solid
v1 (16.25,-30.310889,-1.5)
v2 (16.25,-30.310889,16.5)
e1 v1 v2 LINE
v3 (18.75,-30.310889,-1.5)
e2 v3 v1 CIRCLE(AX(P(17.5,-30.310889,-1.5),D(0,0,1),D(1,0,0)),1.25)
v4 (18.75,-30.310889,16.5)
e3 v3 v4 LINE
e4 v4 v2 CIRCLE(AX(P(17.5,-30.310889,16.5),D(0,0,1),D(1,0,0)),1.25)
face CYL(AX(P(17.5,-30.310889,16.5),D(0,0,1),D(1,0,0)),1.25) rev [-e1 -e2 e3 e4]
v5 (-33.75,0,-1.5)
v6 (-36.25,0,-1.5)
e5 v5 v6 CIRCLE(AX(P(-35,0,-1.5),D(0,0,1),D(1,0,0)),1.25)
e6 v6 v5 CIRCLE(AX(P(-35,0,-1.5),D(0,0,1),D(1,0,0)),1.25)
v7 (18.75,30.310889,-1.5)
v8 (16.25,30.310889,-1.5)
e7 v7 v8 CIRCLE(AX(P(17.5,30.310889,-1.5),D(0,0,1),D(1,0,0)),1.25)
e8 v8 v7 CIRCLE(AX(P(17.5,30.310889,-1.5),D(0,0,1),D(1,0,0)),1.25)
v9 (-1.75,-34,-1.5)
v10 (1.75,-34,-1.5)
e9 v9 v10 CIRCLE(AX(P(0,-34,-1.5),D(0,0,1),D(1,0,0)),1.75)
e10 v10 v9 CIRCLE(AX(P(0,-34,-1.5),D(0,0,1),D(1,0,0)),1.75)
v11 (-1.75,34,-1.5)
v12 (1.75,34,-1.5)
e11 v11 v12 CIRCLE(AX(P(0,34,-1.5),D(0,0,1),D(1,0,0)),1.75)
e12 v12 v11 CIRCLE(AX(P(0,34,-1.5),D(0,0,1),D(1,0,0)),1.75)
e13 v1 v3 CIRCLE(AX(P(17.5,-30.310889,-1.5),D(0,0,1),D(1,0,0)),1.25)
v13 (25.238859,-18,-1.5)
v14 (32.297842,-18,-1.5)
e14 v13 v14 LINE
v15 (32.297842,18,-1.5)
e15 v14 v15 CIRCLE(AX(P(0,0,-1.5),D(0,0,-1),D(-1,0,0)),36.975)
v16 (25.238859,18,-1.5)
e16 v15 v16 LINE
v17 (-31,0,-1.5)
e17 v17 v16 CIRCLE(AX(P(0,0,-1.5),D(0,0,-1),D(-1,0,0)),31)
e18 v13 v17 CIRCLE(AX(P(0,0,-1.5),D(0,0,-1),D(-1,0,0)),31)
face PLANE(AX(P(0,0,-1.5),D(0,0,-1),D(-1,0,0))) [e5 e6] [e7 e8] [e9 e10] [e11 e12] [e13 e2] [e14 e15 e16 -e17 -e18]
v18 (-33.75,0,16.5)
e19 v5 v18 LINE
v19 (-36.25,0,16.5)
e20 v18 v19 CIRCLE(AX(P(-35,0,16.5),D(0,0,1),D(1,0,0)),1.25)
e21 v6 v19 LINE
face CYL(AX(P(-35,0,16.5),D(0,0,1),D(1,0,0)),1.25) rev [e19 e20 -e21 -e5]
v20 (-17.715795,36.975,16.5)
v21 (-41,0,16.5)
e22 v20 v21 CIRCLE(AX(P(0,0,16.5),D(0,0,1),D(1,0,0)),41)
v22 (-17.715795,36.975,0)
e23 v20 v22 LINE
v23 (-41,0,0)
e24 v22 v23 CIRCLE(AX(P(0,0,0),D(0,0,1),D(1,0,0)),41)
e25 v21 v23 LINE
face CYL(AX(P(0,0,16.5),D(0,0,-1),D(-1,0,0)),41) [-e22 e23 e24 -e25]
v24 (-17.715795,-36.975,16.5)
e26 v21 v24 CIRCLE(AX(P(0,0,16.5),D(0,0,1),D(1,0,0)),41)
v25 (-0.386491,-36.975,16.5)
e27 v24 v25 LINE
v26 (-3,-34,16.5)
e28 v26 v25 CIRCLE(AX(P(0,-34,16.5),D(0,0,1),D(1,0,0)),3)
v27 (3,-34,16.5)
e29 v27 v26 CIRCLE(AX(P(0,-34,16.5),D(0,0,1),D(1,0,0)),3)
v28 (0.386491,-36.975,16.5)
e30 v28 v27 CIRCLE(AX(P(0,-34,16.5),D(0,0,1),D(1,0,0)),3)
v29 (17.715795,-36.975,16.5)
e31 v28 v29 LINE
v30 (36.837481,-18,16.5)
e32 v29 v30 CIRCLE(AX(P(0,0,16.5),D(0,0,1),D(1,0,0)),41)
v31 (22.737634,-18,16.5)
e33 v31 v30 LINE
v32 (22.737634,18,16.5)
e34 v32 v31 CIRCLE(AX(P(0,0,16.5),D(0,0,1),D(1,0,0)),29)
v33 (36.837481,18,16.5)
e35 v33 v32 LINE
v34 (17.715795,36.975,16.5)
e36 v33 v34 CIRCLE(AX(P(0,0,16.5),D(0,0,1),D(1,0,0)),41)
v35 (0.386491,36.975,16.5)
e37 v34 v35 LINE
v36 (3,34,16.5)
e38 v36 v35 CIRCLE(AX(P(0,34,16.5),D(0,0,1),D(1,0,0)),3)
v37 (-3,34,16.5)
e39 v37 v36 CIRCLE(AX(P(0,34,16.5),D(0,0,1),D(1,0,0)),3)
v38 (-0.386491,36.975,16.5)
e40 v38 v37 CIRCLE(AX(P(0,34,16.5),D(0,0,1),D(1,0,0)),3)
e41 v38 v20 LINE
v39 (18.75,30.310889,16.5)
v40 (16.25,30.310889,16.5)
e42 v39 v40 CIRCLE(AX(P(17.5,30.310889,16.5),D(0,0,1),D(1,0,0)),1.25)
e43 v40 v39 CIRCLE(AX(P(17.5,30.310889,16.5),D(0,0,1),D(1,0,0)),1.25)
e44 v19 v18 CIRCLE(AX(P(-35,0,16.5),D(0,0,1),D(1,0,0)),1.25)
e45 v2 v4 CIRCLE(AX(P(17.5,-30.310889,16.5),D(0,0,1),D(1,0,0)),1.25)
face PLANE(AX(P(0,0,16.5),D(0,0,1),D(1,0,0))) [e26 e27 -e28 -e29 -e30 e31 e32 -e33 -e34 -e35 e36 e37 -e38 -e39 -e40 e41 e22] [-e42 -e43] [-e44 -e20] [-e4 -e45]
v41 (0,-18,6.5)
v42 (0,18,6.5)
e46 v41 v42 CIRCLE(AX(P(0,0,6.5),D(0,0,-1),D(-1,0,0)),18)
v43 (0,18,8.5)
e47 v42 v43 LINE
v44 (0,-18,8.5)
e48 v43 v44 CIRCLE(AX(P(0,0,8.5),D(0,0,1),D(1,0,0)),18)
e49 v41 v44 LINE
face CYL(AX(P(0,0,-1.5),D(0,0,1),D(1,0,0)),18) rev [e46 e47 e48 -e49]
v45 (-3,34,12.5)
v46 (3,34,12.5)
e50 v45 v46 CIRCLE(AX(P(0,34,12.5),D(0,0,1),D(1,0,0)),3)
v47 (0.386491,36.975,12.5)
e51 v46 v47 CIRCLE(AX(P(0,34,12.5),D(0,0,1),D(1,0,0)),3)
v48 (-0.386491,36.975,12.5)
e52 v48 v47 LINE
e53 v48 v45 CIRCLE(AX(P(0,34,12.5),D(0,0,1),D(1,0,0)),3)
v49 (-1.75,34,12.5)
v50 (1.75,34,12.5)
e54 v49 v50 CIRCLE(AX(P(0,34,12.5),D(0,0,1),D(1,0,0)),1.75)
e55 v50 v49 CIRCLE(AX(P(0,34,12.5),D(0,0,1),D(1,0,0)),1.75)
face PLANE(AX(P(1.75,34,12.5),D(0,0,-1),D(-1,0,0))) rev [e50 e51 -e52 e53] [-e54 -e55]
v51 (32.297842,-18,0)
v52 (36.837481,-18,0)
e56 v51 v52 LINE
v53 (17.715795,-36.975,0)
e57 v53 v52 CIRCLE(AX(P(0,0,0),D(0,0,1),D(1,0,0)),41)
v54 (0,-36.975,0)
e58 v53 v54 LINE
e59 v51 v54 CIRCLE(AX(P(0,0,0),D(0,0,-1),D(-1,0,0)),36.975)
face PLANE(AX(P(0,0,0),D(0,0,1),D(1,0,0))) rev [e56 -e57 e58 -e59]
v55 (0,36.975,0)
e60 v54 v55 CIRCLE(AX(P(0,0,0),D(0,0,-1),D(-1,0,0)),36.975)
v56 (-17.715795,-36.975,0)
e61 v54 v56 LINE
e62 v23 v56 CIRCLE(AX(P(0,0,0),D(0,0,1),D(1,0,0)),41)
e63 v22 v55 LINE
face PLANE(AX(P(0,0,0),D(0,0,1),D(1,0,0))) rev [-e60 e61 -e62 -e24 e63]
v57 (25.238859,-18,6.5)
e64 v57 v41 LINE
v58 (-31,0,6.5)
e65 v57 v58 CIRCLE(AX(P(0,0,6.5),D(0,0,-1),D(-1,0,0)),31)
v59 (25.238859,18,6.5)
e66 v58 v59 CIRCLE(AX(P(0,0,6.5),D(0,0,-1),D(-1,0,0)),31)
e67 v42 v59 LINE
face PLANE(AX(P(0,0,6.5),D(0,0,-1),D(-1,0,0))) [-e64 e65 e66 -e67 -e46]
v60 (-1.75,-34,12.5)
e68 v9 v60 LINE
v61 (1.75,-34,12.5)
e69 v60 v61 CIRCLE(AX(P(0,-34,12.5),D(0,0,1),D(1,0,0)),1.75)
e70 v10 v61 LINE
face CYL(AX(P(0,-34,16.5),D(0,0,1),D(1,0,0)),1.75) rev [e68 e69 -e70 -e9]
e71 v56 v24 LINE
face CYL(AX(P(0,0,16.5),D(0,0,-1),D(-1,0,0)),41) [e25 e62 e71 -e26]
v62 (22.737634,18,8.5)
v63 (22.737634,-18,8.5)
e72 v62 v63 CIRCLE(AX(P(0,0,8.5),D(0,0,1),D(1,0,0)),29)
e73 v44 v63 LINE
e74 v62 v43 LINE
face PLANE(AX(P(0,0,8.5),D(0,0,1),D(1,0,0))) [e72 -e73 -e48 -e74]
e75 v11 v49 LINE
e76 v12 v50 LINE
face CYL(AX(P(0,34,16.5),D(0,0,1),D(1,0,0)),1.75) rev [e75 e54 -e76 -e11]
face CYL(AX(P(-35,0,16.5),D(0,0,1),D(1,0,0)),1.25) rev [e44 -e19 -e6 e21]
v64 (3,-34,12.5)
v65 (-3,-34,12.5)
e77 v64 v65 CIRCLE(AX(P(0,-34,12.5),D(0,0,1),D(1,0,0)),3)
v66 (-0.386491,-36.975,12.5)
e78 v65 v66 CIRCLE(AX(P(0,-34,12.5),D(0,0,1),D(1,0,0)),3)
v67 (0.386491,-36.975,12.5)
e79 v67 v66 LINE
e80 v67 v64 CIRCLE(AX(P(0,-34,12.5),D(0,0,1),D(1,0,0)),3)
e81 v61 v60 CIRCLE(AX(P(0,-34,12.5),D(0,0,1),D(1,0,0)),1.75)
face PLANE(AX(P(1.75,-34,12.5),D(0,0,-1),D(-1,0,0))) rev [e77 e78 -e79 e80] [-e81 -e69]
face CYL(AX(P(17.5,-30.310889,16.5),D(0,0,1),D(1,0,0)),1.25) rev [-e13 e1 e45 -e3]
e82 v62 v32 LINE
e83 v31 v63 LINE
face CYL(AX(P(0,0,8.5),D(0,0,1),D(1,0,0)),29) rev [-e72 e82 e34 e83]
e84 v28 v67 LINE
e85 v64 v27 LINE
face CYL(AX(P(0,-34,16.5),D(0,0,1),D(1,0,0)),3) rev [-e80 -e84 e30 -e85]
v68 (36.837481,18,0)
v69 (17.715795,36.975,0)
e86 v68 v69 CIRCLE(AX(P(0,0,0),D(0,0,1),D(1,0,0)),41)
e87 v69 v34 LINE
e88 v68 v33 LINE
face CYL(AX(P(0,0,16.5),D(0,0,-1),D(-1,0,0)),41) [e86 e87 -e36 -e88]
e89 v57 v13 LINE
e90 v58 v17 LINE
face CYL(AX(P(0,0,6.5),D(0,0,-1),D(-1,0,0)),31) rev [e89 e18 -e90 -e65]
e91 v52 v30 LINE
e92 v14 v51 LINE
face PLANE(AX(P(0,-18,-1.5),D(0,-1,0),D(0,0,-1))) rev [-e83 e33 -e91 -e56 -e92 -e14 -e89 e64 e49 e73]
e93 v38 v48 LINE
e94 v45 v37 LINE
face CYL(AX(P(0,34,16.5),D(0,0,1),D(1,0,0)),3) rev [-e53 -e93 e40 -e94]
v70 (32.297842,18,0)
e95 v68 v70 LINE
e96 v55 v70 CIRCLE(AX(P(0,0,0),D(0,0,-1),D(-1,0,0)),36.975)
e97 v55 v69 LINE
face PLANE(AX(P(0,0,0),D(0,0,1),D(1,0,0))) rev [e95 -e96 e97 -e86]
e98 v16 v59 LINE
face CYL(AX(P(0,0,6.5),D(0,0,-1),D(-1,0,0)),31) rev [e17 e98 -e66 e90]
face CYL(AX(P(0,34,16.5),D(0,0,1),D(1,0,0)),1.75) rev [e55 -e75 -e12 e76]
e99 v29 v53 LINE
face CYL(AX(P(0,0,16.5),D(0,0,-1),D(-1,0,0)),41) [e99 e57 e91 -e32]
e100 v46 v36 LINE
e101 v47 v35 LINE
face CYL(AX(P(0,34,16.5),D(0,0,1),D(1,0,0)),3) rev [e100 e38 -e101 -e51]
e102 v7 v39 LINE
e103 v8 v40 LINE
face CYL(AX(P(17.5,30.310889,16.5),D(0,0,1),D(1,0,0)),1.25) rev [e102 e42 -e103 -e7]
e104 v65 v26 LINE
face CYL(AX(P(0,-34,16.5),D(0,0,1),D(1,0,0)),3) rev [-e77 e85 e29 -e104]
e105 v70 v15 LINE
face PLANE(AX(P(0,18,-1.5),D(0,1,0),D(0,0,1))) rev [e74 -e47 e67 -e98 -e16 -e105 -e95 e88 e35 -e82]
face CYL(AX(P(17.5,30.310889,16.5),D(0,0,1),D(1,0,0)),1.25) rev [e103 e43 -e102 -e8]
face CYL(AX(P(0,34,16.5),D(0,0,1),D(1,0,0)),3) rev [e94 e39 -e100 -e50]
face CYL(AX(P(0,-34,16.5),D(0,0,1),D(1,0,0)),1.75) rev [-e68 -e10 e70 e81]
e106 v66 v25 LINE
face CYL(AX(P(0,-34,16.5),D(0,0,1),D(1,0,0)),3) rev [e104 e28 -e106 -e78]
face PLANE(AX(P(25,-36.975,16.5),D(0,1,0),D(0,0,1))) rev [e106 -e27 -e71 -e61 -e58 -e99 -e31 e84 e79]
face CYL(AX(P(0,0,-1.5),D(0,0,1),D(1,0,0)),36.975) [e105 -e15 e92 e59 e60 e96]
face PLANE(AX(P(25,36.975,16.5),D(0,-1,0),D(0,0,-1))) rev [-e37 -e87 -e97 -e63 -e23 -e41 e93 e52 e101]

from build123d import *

# Parameters (mm, degrees)
SKETCH1_R                               = 41
BOSS_EXTRUDE1_DEPTH                     = 16.5
SKETCH2_R                               = 36.975
BOSS_EXTRUDE2_DEPTH                     = 1.5
SKETCH4_W                               = 50
SKETCH4_H                               = 6.84002239
CUT_EXTRUDE1_DEPTH                      = 61.712436947
SKETCH5_R                               = 31
CUT_EXTRUDE3_DEPTH                      = 8
SKETCH6_R                               = 29
CUT_EXTRUDE4_DEPTH                      = 8
CUT_EXTRUDE5_DEPTH                      = 57.108382841
CUT_EXTRUDE5_DEPTH_BACK                 = 57.108382841
CBORE_FOR_M3_HEX_HEAD_BOLT3_D           = 3.5
CBORE_FOR_M3_HEX_HEAD_BOLT3_CBORE_D     = 6
CBORE_FOR_M3_HEX_HEAD_BOLT3_CBORE_DEPTH = 4
M3_TAPPED_HOLE1_D                       = 2.5
CIRPATTERN1_COUNT                       = 3


with BuildPart() as part:
    # Sketch1 → Boss-Extrude1 (new body)
    with BuildSketch(Plane.XY):
        Circle(SKETCH1_R)
    extrude(amount=BOSS_EXTRUDE1_DEPTH)

    # Sketch2 → Boss-Extrude2 (add)
    with BuildSketch(Plane(origin=(0, 0, 0), x_dir=(-1, 0, 0), z_dir=(0, 0, -1))):
        Circle(SKETCH2_R)
    extrude(amount=BOSS_EXTRUDE2_DEPTH)

    # Sketch4 → Cut-Extrude1 (cut, through all)
    with BuildSketch(Plane(origin=(0, 0, -1.5), x_dir=(-1, 0, 0), z_dir=(0, 0, -1))):
        with Locations((0, 40.395011195)):
            Rectangle(SKETCH4_W, SKETCH4_H)
        with Locations((0, -40.395011195)):
            Rectangle(SKETCH4_W, SKETCH4_H)
    extrude(amount=-CUT_EXTRUDE1_DEPTH, mode=Mode.SUBTRACT)

    # Sketch5 → Cut-Extrude3 (cut)
    with BuildSketch(Plane(origin=(0, 0, -1.5), x_dir=(-1, 0, 0), z_dir=(0, 0, -1))):
        Circle(SKETCH5_R)
    extrude(amount=-CUT_EXTRUDE3_DEPTH, mode=Mode.SUBTRACT)

    # Sketch6 → Cut-Extrude4 (cut)
    with BuildSketch(Plane.XY.offset(16.5)):
        Circle(SKETCH6_R)
    extrude(amount=-CUT_EXTRUDE4_DEPTH, mode=Mode.SUBTRACT)

    # Sketch7 → Cut-Extrude5 (cut, two sides: drawn at the far end of the back side and taken through both)
    with BuildSketch(Plane.XY.offset(8.5).offset(-CUT_EXTRUDE5_DEPTH_BACK)):
        with BuildLine():
            Line((0, 18), (36.837480913, 18))
            ThreePointArc((36.837480913, 18), (41, 0), (36.837480913, -18))
            Line((36.837480913, -18), (0, -18))
            ThreePointArc((0, -18), (-18, 0), (0, 18))
        make_face()
    extrude(amount=CUT_EXTRUDE5_DEPTH + CUT_EXTRUDE5_DEPTH_BACK, mode=Mode.SUBTRACT)

    # CBORE for M3 Hex Head Bolt3 (through all)
    with Locations(Plane(origin=(0, 34, 16.5), x_dir=(1, 0, 0), z_dir=(0, 0, 1))):
        with Locations((0, 0), (0, -68)):
            CounterBoreHole(CBORE_FOR_M3_HEX_HEAD_BOLT3_D / 2, CBORE_FOR_M3_HEX_HEAD_BOLT3_CBORE_D / 2, CBORE_FOR_M3_HEX_HEAD_BOLT3_CBORE_DEPTH)

    # M3 Tapped Hole1 (through all)
    with Locations(Plane(origin=(-35, 0, 16.5), x_dir=(1, 0, 0), z_dir=(0, 0, 1))):
        with Locations((0, 0)):
            m3_tapped_hole1 = Hole(M3_TAPPED_HOLE1_D / 2)

    # CirPattern1: M3 Tapped Hole1 ×3 about axis
    cirpattern1_axis = Axis((0, 0, 0), (0, 0, 1))
    for i in range(1, CIRPATTERN1_COUNT):
        add(m3_tapped_hole1.rotate(cirpattern1_axis, i * 360 / CIRPATTERN1_COUNT), mode=Mode.SUBTRACT)


solid = part.part
